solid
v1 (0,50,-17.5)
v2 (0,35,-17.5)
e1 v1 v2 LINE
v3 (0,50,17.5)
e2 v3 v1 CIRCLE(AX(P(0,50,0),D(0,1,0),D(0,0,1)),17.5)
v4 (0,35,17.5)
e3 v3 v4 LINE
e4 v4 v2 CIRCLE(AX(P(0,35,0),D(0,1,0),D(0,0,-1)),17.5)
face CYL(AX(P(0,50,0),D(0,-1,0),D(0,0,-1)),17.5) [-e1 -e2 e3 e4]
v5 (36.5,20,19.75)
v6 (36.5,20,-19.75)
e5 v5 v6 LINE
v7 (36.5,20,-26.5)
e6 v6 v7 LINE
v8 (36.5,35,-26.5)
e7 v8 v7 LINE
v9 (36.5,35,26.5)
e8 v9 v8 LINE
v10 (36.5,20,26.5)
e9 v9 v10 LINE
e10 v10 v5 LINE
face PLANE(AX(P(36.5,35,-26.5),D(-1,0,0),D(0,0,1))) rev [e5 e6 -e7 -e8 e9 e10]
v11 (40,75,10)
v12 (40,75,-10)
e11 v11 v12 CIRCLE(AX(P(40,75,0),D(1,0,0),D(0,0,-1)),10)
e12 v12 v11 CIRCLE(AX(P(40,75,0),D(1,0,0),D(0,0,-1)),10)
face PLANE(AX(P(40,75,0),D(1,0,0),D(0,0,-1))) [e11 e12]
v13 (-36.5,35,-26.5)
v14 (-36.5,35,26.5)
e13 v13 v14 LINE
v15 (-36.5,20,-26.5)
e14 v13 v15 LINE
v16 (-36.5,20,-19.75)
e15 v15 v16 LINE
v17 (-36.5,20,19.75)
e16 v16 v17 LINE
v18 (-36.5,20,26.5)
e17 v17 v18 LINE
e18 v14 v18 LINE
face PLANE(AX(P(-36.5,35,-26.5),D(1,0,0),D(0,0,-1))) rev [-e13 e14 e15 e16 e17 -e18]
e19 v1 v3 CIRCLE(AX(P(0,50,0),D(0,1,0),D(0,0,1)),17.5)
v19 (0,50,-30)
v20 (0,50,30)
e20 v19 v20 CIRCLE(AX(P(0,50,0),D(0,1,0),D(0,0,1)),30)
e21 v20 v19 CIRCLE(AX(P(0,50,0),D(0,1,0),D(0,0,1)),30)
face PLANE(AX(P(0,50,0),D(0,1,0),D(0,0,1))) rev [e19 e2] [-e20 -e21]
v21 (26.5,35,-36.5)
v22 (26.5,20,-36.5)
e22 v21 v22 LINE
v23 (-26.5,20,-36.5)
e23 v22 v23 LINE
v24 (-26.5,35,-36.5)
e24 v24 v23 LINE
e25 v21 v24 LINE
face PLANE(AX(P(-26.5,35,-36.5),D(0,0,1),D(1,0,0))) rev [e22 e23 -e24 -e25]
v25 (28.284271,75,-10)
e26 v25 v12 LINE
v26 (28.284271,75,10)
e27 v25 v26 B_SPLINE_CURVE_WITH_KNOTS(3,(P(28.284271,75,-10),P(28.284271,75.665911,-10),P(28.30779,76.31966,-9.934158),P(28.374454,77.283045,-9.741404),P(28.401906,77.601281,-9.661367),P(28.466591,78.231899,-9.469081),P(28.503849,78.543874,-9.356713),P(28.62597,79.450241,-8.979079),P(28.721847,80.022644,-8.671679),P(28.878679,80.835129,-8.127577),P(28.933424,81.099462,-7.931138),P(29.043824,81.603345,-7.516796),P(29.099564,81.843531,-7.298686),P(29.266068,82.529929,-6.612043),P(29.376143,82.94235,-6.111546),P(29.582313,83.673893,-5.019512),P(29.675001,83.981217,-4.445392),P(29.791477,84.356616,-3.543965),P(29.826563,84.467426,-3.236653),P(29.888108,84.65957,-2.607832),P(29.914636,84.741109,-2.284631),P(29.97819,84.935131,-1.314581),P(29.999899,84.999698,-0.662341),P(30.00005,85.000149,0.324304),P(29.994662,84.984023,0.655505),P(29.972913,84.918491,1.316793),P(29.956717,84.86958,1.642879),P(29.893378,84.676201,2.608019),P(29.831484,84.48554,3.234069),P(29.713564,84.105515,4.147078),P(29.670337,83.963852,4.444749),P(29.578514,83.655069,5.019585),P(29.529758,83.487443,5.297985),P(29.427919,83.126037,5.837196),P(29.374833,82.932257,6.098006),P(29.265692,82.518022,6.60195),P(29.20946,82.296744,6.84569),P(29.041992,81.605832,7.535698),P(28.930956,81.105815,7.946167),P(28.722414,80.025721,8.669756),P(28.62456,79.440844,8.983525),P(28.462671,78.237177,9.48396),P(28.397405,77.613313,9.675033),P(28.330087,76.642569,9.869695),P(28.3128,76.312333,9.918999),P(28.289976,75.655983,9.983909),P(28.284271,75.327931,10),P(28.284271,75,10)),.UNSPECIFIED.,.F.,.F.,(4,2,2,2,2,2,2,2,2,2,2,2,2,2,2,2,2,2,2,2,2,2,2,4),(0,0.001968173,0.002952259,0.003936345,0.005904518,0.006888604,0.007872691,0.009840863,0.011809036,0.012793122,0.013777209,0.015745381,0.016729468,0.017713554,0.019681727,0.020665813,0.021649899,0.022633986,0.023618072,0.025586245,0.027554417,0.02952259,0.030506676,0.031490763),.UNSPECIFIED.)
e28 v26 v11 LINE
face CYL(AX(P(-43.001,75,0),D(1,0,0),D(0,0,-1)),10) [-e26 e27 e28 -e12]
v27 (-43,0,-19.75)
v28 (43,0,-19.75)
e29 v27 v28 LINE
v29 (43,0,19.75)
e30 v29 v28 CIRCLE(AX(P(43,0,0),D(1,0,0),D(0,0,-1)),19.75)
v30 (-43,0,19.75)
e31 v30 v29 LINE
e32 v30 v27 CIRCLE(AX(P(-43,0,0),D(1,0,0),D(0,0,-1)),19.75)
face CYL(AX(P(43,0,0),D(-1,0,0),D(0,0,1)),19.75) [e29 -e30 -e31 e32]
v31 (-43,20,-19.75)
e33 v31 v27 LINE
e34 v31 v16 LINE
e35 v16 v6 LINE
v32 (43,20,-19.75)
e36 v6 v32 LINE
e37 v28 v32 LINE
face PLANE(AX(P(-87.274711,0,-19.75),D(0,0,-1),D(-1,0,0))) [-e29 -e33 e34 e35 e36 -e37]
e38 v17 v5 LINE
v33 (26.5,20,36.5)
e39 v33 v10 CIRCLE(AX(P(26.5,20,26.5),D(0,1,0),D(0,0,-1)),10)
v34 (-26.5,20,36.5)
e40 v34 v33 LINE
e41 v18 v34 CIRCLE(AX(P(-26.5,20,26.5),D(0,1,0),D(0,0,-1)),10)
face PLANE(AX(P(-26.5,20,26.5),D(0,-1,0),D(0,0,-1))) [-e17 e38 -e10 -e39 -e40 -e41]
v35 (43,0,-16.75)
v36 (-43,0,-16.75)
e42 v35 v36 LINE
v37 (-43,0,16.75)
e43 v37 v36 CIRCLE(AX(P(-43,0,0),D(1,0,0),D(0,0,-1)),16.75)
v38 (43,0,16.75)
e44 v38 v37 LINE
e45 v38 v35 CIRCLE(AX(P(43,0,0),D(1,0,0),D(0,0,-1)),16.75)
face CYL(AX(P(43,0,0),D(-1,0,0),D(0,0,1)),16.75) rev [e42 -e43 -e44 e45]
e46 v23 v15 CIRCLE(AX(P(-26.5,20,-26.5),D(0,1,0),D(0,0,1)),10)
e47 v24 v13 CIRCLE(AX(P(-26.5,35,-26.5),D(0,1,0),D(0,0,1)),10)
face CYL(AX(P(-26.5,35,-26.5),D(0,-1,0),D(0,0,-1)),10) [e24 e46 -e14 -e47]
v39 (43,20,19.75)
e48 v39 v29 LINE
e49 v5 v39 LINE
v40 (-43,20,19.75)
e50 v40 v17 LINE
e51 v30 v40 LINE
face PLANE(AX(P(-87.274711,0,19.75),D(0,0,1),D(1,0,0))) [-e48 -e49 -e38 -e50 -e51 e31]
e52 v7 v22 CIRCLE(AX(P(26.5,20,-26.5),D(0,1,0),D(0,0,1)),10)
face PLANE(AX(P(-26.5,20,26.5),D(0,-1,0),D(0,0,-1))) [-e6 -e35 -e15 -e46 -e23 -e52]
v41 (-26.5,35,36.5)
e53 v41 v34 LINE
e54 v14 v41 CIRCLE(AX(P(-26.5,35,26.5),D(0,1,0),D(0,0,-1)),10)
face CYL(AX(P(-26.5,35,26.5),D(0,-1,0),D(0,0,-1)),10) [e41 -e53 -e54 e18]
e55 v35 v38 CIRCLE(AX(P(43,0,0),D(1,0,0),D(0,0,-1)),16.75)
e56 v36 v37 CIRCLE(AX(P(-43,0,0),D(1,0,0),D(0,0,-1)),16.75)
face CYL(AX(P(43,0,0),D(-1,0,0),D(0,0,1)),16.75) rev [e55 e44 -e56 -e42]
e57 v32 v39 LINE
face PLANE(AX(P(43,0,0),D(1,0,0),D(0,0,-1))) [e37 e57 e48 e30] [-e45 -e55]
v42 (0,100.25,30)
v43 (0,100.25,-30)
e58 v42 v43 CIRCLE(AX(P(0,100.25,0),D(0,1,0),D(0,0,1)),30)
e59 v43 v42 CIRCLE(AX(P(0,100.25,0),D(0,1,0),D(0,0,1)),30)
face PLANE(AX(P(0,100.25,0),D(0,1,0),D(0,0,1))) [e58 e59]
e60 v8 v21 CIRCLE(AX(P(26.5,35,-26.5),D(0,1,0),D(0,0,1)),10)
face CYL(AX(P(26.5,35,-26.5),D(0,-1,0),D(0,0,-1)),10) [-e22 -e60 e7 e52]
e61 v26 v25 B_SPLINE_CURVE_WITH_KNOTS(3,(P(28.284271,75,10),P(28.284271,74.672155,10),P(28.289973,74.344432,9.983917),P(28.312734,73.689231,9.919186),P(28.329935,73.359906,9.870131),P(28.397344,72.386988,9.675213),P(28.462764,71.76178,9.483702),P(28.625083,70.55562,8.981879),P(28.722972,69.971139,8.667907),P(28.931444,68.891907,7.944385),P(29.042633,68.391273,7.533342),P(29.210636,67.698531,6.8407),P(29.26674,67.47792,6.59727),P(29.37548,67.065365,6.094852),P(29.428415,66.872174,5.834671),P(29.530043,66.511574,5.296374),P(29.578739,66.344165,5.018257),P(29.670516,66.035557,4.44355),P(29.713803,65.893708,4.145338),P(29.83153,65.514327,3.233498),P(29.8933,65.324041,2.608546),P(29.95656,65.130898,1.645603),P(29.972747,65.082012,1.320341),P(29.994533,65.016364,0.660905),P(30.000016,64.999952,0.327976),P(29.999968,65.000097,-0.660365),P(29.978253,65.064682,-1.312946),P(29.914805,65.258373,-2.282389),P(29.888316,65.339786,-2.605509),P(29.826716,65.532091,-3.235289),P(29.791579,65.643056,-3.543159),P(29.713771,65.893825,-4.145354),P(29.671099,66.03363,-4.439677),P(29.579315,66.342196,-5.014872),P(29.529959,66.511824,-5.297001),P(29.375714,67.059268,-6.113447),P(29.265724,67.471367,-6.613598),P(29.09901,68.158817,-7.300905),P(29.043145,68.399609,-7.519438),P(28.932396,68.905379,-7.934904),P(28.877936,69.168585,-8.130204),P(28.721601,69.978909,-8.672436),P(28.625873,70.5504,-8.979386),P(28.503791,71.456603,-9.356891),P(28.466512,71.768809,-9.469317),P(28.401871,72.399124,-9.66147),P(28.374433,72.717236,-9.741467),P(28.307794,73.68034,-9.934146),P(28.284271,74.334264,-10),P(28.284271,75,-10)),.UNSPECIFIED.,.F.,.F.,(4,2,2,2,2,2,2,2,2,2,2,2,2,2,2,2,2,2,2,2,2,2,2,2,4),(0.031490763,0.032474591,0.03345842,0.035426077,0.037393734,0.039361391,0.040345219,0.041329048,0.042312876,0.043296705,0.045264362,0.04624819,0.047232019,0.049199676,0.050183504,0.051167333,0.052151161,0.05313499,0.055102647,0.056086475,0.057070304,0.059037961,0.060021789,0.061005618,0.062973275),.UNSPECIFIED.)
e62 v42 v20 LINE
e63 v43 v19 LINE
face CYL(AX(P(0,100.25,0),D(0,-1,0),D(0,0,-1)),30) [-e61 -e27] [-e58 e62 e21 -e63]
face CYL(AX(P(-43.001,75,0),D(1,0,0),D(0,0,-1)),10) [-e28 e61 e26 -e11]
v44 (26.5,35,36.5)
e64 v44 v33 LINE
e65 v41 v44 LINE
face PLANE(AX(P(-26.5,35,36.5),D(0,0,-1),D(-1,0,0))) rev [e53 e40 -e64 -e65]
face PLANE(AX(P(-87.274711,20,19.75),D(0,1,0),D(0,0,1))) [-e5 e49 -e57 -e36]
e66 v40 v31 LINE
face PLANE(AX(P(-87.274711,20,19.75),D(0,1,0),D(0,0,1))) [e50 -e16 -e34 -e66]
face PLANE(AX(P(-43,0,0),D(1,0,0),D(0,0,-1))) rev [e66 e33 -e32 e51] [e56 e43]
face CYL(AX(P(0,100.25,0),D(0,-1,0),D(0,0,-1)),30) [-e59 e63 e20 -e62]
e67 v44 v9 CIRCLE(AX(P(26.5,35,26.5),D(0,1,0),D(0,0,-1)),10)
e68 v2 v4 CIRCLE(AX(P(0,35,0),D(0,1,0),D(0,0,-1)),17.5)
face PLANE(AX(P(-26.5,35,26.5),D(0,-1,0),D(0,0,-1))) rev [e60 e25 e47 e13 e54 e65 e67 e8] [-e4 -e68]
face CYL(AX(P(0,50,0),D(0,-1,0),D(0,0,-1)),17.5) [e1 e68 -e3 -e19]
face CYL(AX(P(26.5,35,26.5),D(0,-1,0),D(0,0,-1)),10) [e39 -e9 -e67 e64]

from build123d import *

# Parameters (mm, degrees)
SKETCH_1_R           = 19.75
SKETCH_1_R_2         = 16.75
EXTRUDE_1_DEPTH      = 43
EXTRUDE_1_2_DEPTH    = 15
SKETCH_4_R           = 17.5
EXTRUDE_2_DEPTH      = 15
SKETCH_5_R           = 30
EXTRUDE_3_DEPTH      = 50.25
EXTRUDE_START        = -86
EXTRUDE_4_DEPTH      = 86
EXTRUDE_5_REACH      = 137.171
EXTRUDE_5_END_RADIUS = 30
SKETCH_7_R           = 10


with BuildPart() as part:
    # 草图1 → Extrude 1 (new, symmetric)
    with BuildSketch(Plane(origin=(0, 0, 0), x_dir=(0, 0, -1), z_dir=(1, 0, 0))):
        Circle(SKETCH_1_R)
        Circle(SKETCH_1_R_2, mode=Mode.SUBTRACT)
    extrude(amount=EXTRUDE_1_DEPTH, both=True)



with BuildPart() as body_2:
    # 草图3 → Extrude 1 2 (new body)
    with BuildSketch(Plane(origin=(0, 20, 0), x_dir=(1, 0, 0), z_dir=(0, 1, 0))):
        with BuildLine():
            Line((-26.5, 36.5), (26.5, 36.5))
            ThreePointArc((26.5, 36.5), (33.571067812, 33.571067812), (36.5, 26.5))
            Line((36.5, 26.5), (36.5, -26.5))
            ThreePointArc((36.5, -26.5), (33.571067812, -33.571067812), (26.5, -36.5))
            Line((26.5, -36.5), (-26.5, -36.5))
            ThreePointArc((-26.5, -36.5), (-33.571067812, -33.571067812), (-36.5, -26.5))
            Line((-36.5, -26.5), (-36.5, 26.5))
            ThreePointArc((-36.5, 26.5), (-33.571067812, 33.571067812), (-26.5, 36.5))
        make_face()
    extrude(amount=EXTRUDE_1_2_DEPTH)

    # 草图4 → 凸台-拉伸2 (add)
    with BuildSketch(Plane(origin=(0, 35, 0), x_dir=(1, 0, 0), z_dir=(0, 1, 0))):
        with Locations(Location((0, 0, 0), (0, 0, 90))):
            Circle(SKETCH_4_R)
    extrude(amount=EXTRUDE_2_DEPTH)

    # 草图5 → 凸台-拉伸3 (add)
    with BuildSketch(Plane(origin=(0, 50, 0), x_dir=(1, 0, 0), z_dir=(0, 1, 0))):
        with Locations(Location((0, 0, 0), (0, 0, 270))):
            Circle(SKETCH_5_R)
    extrude(amount=EXTRUDE_3_DEPTH)


with BuildPart() as part_1:
    add(part.part)

    add(body_2.part)  # 凸台-拉伸4 merges body 2
    # 草图6 → 凸台-拉伸4 (add)
    with BuildSketch(Plane(origin=(43, 0, 0), x_dir=(0, 0, -1), z_dir=(1, 0, 0)).offset(EXTRUDE_START)):
        with BuildLine():
            Line((-19.75, 0), (-19.75, 20))
            Line((-19.75, 20), (19.75, 20))
            Line((19.75, 20), (19.75, 0))
            ThreePointArc((19.75, 0), (0, 19.75), (-19.75, 0))
        make_face()
    extrude(amount=EXTRUDE_4_DEPTH)

    # 凸台-拉伸5: up to this cylinder (the profile starts outside it)
    extrude_5_end = Plane(origin=(0, 75, 0), z_dir=(0, -1, 0)) * Cylinder(EXTRUDE_5_END_RADIUS, 335.342, mode=Mode.PRIVATE)
    # 草图7 → 凸台-拉伸5 (add, up to the surface)
    with BuildSketch(Plane(origin=(40, 0, 0), x_dir=(0, 0, -1), z_dir=(1, 0, 0)), mode=Mode.PRIVATE) as extrude_5_sk1:
        with Locations((0, 75)):
            Circle(SKETCH_7_R)
    extrude_5_tool1 = extrude(extrude_5_sk1.sketch, amount=-EXTRUDE_5_REACH, mode=Mode.PRIVATE) - extrude_5_end
    add(extrude_5_tool1.solids().sort_by_distance((40, 75, 0))[0])


solid = part_1.part
